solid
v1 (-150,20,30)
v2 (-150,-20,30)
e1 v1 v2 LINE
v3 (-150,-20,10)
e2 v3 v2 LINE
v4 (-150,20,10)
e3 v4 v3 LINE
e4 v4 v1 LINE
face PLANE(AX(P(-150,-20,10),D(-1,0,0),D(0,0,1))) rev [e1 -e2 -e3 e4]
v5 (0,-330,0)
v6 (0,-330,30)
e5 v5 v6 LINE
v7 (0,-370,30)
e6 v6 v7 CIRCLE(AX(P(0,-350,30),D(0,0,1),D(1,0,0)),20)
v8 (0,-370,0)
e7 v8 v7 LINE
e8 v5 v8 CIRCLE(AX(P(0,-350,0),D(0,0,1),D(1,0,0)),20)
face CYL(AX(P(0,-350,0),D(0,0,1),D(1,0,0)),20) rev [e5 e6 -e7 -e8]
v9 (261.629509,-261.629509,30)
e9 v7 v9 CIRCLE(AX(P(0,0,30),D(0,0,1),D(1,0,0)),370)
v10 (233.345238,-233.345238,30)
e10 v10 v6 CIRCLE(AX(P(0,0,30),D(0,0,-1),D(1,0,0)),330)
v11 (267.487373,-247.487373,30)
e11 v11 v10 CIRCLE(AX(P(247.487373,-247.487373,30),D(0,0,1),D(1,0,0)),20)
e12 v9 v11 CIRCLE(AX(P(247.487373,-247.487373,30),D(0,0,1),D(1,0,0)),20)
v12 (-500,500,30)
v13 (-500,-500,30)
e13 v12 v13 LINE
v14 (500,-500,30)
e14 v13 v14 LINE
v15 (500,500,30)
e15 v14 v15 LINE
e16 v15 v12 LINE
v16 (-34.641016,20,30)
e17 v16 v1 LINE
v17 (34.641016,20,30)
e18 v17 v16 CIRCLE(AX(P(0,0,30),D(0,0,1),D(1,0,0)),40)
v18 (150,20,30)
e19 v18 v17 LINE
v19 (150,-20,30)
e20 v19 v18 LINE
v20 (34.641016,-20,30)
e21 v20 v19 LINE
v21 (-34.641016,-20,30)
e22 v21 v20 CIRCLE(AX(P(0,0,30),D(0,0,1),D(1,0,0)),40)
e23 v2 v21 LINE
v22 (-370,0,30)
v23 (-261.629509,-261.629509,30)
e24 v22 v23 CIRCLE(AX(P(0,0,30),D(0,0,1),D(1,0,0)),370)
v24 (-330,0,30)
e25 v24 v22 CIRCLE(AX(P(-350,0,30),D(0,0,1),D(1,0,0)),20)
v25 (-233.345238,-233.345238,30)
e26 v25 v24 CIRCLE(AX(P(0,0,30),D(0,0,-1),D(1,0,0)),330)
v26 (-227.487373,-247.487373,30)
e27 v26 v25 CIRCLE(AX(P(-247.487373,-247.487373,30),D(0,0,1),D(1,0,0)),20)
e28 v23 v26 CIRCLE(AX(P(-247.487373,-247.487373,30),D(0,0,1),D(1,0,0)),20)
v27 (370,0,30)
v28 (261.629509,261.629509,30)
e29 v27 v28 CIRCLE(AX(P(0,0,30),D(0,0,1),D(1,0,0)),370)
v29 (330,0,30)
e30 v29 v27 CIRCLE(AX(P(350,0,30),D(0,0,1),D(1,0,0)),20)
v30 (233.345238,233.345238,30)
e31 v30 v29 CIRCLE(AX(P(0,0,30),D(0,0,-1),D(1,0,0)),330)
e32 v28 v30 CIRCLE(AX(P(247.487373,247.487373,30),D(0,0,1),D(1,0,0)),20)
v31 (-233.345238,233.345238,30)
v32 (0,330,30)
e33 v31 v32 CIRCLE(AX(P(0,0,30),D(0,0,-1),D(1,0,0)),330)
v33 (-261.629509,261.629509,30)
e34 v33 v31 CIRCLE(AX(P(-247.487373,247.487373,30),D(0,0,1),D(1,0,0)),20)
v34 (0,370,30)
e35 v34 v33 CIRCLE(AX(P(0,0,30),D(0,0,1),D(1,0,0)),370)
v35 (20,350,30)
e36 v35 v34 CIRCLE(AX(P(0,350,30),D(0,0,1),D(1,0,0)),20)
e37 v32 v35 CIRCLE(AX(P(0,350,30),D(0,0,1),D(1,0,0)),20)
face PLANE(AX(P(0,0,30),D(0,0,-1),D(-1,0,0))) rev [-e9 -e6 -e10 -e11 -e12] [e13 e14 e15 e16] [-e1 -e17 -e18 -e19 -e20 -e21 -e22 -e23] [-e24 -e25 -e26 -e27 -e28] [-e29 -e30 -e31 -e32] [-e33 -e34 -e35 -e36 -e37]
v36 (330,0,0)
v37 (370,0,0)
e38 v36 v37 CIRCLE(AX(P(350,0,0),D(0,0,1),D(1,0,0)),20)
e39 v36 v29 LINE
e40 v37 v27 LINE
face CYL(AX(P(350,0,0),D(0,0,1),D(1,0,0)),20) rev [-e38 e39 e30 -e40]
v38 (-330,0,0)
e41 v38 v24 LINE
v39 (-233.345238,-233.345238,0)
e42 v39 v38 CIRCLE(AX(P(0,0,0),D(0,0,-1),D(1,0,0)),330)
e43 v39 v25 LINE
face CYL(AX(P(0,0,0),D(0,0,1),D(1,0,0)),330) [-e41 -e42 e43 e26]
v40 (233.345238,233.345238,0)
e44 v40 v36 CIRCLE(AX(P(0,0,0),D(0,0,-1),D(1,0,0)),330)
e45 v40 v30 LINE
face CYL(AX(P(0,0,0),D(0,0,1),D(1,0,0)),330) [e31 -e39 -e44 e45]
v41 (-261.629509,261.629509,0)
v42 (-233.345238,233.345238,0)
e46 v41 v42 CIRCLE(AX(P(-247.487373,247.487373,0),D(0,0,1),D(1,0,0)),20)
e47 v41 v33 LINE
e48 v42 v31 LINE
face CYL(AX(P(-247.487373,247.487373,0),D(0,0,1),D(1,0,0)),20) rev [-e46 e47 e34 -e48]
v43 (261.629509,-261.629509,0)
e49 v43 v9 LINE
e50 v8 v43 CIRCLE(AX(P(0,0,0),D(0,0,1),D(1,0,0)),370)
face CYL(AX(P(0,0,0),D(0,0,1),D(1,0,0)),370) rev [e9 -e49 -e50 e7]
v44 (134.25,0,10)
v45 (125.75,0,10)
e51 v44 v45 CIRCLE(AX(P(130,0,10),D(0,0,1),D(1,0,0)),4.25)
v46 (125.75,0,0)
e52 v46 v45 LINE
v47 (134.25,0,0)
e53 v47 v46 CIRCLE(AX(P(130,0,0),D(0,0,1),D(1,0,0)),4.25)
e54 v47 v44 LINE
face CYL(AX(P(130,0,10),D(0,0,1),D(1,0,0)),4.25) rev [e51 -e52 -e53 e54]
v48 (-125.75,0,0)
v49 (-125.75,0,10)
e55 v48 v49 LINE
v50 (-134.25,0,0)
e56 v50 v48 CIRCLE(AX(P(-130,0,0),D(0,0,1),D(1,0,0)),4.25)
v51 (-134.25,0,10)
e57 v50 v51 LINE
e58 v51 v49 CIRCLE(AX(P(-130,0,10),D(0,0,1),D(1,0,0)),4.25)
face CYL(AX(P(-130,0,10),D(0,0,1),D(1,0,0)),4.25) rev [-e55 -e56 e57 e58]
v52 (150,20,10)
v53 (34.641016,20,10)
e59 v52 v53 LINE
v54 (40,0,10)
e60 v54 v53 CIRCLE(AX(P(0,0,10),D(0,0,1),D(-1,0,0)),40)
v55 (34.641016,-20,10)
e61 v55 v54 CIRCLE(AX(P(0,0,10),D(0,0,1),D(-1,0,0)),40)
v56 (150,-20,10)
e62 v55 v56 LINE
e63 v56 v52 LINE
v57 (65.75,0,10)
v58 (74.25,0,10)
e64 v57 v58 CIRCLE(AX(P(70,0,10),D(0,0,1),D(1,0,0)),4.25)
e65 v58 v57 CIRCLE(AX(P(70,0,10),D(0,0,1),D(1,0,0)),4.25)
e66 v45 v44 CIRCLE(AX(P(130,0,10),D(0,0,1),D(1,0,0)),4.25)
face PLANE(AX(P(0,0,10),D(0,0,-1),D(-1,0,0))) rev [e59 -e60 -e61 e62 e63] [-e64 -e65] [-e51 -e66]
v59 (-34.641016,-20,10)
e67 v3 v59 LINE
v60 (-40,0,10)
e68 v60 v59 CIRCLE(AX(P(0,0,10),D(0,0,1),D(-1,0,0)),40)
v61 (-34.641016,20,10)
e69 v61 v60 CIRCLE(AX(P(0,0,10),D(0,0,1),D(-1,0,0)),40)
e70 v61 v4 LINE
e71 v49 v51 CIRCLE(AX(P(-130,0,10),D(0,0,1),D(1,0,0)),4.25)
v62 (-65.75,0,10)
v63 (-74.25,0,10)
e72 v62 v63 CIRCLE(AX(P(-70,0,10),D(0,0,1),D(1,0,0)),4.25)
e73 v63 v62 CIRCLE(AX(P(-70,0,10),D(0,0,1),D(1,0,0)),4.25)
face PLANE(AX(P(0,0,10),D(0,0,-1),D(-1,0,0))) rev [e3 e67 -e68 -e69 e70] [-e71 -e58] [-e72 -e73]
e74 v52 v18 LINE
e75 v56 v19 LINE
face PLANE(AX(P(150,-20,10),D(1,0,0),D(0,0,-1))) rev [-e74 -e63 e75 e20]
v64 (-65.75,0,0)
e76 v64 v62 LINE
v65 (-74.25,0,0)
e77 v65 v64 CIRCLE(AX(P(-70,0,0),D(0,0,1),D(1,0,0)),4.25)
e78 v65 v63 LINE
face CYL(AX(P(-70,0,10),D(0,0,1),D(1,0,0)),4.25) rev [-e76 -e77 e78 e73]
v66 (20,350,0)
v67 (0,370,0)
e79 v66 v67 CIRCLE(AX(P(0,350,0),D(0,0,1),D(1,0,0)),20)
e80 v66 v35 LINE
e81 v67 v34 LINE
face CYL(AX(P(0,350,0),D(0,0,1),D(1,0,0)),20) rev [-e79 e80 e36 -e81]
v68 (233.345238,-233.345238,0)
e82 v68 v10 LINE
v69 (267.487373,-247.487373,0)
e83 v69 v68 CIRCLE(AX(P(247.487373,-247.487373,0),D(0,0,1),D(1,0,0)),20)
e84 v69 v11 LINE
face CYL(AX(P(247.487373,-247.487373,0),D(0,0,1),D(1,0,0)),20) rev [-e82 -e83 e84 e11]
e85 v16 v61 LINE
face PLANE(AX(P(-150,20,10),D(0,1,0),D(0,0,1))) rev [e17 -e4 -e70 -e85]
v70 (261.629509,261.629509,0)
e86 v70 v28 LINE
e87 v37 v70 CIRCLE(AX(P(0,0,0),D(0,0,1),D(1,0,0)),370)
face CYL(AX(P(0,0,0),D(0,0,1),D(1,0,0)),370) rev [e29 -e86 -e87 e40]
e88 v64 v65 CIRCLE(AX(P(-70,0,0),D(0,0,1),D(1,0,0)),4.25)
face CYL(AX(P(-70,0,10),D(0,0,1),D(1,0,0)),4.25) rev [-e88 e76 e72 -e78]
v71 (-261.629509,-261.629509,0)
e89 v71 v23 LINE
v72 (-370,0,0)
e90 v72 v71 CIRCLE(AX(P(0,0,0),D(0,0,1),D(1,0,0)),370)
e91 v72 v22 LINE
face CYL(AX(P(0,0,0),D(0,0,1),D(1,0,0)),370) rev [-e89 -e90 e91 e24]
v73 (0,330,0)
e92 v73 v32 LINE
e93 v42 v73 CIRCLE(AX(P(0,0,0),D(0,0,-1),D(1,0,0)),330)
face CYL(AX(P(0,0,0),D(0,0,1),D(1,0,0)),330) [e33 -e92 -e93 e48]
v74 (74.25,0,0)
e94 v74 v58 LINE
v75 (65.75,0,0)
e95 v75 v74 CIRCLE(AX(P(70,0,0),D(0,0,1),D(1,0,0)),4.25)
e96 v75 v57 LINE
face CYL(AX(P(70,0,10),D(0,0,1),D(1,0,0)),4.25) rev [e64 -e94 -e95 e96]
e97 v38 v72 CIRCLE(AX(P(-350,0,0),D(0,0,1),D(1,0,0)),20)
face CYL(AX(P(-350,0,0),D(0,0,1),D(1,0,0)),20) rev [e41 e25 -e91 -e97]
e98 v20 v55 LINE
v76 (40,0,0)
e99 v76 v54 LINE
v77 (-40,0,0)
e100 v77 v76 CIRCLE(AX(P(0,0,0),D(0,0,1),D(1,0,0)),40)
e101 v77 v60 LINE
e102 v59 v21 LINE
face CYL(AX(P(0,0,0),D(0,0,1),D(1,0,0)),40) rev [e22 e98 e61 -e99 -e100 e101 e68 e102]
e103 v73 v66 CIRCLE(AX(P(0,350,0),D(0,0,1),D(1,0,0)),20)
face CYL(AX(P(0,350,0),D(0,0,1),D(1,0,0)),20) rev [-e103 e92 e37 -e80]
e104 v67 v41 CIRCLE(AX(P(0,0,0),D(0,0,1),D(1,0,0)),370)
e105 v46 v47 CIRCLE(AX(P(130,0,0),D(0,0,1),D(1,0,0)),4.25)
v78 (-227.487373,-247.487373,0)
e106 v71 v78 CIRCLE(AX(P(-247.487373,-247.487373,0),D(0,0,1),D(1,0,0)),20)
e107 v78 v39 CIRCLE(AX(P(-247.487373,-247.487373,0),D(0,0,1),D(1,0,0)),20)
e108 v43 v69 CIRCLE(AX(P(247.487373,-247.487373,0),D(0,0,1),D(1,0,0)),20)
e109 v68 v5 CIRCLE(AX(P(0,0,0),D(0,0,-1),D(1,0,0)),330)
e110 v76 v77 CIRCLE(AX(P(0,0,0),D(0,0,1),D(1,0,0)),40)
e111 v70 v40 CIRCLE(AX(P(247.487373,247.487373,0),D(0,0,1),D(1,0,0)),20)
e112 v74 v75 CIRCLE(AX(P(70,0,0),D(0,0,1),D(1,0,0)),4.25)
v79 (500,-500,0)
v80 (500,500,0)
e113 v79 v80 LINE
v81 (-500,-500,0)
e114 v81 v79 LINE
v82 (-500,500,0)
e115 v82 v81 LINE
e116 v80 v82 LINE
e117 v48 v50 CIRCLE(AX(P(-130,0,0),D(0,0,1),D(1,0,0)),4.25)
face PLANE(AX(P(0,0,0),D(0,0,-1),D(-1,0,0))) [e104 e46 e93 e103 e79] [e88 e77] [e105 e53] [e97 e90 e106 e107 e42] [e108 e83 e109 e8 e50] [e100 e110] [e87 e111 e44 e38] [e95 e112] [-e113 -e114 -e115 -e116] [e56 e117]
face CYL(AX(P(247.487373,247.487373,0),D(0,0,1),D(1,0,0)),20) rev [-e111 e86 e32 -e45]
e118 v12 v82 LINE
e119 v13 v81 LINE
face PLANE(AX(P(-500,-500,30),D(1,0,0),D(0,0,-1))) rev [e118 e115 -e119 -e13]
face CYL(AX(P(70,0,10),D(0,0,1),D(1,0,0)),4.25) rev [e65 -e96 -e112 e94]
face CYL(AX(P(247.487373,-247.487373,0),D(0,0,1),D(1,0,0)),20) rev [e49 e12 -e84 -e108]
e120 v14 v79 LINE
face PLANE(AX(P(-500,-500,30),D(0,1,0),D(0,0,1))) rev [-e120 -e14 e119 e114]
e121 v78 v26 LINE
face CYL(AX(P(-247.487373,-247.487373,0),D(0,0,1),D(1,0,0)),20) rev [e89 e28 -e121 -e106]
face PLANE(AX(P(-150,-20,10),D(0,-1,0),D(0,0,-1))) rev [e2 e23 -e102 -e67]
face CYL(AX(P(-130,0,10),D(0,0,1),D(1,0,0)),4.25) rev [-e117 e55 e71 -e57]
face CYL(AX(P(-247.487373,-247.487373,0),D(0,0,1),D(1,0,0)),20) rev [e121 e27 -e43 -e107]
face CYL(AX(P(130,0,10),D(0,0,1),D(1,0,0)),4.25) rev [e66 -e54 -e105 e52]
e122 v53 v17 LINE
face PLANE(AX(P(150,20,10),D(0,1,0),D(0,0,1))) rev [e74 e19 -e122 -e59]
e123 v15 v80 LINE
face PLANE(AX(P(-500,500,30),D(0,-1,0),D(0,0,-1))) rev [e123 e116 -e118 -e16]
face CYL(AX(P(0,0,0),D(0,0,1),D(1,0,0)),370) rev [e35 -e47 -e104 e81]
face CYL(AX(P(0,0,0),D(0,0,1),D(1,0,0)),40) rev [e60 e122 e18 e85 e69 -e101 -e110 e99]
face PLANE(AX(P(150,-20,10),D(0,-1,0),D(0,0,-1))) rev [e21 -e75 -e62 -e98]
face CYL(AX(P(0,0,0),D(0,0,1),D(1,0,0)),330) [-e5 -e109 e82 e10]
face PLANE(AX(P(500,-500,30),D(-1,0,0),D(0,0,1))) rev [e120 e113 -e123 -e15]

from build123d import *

# Parameters (mm, degrees)
SKETCH1_W           = 1000
SKETCH1_H           = 1000
BOSS_EXTRUDE1_DEPTH = 30
CUT_EXTRUDE1_DEPTH  = 708.742891169
SKETCH3_R           = 40
CUT_EXTRUDE2_DEPTH  = 708.742891169
SKETCH4_W           = 120
SKETCH4_H           = 40
CUT_EXTRUDE3_DEPTH  = 20
M10_TAPPED_HOLE1_D  = 8.5


with BuildPart() as part:
    # Sketch1 → Boss-Extrude1 (new body)
    with BuildSketch(Plane.XY):
        Rectangle(SKETCH1_W, SKETCH1_H)
    extrude(amount=BOSS_EXTRUDE1_DEPTH)

    # Sketch2 → Cut-Extrude1 (cut, through all)
    with BuildSketch(Plane.XY.offset(30)):
        with BuildLine():
            ThreePointArc((0, 370), (-141.592869975, 341.835427029), (-261.629509039, 261.629509039))
            ThreePointArc((-261.629509039, 261.629509039), (-261.629509039, 233.345237792), (-233.345237792, 233.345237792))
            ThreePointArc((-233.345237792, 233.345237792), (-126.28553268, 304.880245729), (0, 330))
            ThreePointArc((0, 330), (20, 350), (0, 370))
        make_face()
        with BuildLine():
            ThreePointArc((370, 0), (341.835427029, 141.592869975), (261.629509039, 261.629509039))
            ThreePointArc((261.629509039, 261.629509039), (233.345237792, 261.629509039), (233.345237792, 233.345237792))
            ThreePointArc((233.345237792, 233.345237792), (304.880245729, 126.28553268), (330, 0))
            ThreePointArc((330, 0), (350, -20), (370, 0))
        make_face()
        with BuildLine():
            ThreePointArc((0, -370), (141.592869975, -341.835427029), (261.629509039, -261.629509039))
            ThreePointArc((261.629509039, -261.629509039), (261.629509039, -233.345237792), (233.345237792, -233.345237792))
            ThreePointArc((233.345237792, -233.345237792), (126.28553268, -304.880245729), (0, -330))
            ThreePointArc((0, -330), (-20, -350), (0, -370))
        make_face()
        with BuildLine():
            ThreePointArc((-370, 0), (-341.835427029, -141.592869975), (-261.629509039, -261.629509039))
            ThreePointArc((-261.629509039, -261.629509039), (-233.345237792, -261.629509039), (-233.345237792, -233.345237792))
            ThreePointArc((-233.345237792, -233.345237792), (-304.880245729, -126.28553268), (-330, 0))
            ThreePointArc((-330, 0), (-350, 20), (-370, 0))
        make_face()
    extrude(amount=-CUT_EXTRUDE1_DEPTH, mode=Mode.SUBTRACT)

    # Sketch3 → Cut-Extrude2 (cut, through all)
    with BuildSketch(Plane.XY.offset(30)):
        Circle(SKETCH3_R)
    extrude(amount=-CUT_EXTRUDE2_DEPTH, mode=Mode.SUBTRACT)

    # Sketch4 → Cut-Extrude3 (cut)
    with BuildSketch(Plane.XY.offset(30)):
        with Locations((-90, 0)):
            Rectangle(SKETCH4_W, SKETCH4_H)
        with Locations((90, 0)):
            Rectangle(SKETCH4_W, SKETCH4_H)
    extrude(amount=-CUT_EXTRUDE3_DEPTH, mode=Mode.SUBTRACT)

    # M10 Tapped Hole1 (through all)
    with Locations(Plane.XY.offset(10)):
        with Locations((-130, 0), (-70, 0), (70, 0), (130, 0)):
            Hole(M10_TAPPED_HOLE1_D / 2)


solid = part.part
